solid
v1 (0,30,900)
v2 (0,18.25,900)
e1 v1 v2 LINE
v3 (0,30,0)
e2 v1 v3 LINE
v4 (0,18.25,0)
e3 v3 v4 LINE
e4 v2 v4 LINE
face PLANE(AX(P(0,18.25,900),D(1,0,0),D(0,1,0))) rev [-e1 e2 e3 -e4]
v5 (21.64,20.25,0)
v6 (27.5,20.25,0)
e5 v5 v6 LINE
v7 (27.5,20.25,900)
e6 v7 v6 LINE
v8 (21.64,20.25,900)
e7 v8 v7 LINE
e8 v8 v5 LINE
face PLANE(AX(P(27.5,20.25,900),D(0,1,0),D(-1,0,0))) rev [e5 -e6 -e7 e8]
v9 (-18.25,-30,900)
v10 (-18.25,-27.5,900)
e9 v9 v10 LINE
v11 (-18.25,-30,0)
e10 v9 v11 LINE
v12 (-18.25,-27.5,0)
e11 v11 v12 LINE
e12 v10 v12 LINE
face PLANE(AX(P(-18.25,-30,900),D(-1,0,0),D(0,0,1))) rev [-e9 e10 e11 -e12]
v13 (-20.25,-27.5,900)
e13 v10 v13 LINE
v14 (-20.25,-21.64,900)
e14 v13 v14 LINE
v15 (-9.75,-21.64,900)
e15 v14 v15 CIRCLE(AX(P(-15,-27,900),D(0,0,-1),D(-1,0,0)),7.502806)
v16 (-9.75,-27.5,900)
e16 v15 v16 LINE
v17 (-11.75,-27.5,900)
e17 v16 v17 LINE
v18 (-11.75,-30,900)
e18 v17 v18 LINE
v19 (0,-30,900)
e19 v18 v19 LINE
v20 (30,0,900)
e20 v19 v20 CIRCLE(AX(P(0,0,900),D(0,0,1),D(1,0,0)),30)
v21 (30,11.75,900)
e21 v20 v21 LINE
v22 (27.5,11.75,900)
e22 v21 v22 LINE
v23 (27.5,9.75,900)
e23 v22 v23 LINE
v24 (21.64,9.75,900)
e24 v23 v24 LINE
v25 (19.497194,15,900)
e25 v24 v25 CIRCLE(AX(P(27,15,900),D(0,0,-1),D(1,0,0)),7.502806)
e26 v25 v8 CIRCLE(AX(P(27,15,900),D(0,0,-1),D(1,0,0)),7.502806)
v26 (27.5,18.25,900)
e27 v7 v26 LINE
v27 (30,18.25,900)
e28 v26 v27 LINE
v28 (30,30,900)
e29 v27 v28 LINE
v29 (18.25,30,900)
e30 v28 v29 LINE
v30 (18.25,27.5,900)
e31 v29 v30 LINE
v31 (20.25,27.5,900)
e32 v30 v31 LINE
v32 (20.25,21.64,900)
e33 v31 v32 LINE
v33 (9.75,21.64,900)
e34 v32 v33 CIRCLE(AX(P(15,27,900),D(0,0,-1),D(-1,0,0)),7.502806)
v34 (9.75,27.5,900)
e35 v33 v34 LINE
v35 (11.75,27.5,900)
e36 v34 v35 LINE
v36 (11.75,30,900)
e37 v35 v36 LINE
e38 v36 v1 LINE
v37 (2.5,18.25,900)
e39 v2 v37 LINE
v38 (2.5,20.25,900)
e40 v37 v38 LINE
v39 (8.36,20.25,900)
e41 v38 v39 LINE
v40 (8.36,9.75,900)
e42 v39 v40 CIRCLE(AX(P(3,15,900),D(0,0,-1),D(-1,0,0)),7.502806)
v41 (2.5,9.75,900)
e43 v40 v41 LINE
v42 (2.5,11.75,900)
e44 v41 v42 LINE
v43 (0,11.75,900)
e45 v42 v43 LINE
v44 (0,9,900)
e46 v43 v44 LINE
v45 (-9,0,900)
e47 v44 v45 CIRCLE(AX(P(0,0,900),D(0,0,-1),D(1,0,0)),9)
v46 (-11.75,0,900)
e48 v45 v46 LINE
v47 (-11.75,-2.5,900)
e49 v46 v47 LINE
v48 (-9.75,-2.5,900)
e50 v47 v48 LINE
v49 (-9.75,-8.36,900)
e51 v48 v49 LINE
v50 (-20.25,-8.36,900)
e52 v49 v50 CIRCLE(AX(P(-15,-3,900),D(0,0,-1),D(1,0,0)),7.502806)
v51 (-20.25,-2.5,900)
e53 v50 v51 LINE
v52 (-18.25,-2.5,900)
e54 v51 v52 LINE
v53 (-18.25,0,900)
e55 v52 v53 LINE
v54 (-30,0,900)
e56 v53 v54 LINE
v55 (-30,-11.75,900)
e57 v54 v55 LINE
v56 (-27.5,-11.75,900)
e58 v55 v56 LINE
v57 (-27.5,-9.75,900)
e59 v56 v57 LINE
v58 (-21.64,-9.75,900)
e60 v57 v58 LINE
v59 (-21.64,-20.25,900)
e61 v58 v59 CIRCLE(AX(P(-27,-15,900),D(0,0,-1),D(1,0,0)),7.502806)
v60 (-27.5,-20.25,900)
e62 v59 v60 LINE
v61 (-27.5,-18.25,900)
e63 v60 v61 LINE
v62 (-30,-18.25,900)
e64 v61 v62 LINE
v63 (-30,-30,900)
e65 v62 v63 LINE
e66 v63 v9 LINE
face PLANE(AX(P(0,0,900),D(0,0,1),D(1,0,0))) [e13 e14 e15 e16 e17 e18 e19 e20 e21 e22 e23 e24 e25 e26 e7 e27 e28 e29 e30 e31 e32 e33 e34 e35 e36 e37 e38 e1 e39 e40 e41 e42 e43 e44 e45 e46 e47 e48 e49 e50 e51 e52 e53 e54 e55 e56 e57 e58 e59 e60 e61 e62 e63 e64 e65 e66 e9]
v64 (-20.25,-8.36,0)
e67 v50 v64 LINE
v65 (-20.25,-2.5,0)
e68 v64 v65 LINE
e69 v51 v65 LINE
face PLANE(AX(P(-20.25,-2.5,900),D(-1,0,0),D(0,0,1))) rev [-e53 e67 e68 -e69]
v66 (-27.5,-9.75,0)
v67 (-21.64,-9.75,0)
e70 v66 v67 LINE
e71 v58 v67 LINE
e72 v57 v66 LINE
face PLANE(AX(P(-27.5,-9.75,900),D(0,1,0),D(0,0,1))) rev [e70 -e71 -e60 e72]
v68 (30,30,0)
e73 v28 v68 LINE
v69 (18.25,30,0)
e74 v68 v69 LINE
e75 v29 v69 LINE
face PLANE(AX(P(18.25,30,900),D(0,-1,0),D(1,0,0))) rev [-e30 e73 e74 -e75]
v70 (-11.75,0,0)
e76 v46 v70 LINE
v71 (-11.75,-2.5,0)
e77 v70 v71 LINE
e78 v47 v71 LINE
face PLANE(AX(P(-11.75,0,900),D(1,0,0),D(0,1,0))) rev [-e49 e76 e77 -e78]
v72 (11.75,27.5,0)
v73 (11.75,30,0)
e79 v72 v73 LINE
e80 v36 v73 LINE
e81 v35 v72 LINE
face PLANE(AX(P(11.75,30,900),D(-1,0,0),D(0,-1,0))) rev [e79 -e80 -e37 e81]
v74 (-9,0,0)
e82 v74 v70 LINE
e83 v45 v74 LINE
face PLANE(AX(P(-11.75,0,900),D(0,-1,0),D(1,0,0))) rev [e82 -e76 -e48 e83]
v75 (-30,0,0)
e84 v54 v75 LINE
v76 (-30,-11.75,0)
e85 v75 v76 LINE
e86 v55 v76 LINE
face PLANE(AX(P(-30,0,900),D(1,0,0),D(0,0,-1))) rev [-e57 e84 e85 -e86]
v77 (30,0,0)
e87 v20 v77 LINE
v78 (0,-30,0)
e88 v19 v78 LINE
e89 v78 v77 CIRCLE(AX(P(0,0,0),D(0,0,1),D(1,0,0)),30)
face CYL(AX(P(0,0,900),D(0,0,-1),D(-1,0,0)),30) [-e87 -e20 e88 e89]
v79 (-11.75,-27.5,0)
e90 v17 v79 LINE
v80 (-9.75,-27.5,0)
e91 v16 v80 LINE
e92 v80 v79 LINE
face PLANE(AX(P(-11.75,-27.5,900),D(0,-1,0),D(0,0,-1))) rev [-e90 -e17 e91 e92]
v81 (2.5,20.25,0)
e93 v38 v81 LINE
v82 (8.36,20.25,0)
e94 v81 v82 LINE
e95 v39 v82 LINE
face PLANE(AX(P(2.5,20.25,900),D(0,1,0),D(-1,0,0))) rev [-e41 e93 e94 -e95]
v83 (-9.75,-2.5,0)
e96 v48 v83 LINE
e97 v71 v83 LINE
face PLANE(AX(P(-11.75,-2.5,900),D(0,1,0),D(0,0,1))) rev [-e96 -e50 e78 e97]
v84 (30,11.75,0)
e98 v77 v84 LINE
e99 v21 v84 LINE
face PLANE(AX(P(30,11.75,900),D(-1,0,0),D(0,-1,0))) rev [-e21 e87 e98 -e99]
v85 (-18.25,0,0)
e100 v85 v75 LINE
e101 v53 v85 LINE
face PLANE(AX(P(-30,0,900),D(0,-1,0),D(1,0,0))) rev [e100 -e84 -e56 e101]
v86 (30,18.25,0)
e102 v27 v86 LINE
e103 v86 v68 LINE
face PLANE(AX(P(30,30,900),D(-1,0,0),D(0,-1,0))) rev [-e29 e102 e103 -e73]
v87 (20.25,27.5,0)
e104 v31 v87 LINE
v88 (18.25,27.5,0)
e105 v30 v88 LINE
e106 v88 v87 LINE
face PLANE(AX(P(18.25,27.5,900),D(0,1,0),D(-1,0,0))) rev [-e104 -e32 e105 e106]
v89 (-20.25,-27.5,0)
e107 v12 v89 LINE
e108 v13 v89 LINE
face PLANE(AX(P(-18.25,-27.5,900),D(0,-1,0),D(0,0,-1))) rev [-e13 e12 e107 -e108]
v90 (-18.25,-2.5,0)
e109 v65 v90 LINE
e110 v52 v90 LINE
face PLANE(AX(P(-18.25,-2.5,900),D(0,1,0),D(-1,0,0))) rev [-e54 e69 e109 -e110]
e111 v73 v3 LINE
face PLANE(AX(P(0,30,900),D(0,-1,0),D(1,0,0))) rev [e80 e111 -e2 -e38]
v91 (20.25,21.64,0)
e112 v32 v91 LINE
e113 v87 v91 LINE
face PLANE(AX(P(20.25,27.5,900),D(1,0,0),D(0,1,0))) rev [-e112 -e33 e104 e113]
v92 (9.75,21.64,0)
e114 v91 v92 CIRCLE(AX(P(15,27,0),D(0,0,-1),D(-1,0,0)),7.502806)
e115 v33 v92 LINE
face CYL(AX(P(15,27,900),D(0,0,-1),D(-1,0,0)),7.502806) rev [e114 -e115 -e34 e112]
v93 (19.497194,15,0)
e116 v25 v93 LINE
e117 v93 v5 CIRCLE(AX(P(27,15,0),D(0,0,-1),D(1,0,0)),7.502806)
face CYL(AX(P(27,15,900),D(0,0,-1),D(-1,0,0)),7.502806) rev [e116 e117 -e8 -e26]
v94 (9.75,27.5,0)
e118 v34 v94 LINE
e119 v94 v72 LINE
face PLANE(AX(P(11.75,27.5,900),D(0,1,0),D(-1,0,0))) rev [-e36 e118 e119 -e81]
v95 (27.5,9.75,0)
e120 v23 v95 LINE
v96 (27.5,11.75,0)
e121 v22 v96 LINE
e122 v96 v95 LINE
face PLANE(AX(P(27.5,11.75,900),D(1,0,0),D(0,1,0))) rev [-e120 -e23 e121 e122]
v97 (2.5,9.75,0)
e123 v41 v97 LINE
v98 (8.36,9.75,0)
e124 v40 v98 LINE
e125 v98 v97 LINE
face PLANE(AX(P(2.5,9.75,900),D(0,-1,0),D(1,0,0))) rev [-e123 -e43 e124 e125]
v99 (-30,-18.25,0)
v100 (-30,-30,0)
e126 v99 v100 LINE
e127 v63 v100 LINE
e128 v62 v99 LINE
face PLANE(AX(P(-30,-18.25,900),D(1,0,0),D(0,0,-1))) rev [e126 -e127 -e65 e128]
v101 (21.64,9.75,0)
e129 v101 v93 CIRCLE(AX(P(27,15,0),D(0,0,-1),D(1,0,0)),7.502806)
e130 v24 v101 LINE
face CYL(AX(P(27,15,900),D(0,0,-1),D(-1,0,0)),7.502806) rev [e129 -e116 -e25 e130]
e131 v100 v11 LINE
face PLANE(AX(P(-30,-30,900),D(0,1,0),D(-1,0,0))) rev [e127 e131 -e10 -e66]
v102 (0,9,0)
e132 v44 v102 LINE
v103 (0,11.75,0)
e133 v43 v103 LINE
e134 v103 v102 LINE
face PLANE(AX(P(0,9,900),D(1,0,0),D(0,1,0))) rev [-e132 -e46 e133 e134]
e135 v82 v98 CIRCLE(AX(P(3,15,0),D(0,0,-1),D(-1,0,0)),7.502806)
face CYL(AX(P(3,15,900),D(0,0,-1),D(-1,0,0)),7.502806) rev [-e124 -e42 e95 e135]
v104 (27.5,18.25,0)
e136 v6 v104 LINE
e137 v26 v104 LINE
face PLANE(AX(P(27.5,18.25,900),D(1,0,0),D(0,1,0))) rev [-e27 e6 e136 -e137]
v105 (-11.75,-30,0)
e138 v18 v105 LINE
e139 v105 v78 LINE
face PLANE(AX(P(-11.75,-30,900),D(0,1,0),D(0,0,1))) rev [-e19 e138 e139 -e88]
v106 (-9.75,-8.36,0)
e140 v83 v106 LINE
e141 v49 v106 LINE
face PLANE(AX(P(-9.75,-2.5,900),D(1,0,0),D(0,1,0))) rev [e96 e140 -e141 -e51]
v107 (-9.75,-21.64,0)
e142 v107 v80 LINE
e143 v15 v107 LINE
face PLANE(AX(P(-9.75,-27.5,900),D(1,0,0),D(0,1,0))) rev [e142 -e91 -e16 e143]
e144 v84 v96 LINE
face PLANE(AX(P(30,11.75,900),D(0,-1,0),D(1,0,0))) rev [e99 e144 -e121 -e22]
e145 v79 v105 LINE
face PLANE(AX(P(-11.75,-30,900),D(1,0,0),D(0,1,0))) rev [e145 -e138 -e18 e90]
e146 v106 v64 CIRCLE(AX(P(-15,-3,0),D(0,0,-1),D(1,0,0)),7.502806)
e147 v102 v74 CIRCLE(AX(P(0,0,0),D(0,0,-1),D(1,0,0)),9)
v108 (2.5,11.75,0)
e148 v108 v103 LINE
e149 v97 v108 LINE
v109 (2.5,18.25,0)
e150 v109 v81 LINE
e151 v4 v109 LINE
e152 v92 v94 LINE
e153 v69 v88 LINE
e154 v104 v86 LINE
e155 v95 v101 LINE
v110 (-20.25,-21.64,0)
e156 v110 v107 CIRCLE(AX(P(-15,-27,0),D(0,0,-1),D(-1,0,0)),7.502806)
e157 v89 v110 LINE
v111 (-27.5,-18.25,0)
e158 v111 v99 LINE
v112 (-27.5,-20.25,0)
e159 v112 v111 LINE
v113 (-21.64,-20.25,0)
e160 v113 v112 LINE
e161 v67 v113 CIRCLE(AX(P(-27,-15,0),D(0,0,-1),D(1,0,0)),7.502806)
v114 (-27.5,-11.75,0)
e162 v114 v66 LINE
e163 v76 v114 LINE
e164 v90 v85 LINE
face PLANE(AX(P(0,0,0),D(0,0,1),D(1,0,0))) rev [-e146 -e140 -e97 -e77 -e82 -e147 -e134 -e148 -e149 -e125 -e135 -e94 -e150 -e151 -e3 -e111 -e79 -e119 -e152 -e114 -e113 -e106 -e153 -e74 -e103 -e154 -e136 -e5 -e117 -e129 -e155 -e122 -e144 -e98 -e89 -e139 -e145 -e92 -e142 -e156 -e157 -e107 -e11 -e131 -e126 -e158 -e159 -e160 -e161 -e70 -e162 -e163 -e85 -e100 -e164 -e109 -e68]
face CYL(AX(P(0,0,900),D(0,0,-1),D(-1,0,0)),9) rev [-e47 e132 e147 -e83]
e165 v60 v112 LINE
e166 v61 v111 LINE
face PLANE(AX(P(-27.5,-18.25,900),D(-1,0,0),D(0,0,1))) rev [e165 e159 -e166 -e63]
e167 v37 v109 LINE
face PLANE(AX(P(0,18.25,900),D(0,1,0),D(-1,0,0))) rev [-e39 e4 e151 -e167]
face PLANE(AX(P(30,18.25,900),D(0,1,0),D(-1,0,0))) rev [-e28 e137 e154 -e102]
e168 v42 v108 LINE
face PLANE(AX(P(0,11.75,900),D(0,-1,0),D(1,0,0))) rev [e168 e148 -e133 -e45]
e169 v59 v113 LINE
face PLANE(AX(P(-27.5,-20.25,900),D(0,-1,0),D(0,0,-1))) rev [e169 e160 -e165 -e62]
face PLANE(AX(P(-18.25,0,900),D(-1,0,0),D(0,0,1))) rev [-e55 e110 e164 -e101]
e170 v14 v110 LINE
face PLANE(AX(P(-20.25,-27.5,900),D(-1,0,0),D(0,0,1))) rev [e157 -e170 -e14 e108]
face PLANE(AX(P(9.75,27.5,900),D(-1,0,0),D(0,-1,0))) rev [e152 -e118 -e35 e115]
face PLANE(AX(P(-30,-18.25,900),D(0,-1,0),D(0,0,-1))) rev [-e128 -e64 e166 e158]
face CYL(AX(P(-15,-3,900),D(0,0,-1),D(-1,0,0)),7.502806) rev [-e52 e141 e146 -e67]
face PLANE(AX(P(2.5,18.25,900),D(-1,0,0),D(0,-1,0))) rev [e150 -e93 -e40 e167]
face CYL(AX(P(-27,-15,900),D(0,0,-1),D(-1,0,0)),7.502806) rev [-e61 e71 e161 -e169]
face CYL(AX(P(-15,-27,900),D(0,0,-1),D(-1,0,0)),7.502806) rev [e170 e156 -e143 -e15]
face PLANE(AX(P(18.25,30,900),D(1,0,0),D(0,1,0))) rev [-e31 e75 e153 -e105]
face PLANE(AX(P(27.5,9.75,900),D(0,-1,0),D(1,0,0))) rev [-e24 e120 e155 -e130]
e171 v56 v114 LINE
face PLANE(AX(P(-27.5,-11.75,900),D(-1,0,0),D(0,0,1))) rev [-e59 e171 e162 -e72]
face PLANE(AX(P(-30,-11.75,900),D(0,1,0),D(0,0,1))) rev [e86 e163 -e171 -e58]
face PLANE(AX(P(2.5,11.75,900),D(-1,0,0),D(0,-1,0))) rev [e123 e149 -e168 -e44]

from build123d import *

# Parameters (mm, degrees)
EXTRUDE_1_DEPTH = 900


with BuildPart() as part:
    # 草图1 → 凸台-拉伸1 (new body)
    with BuildSketch(Plane.XY):
        with BuildLine():
            Line((0, 9), (0, 11.75))
            Line((0, 11.75), (2.5, 11.75))
            Line((2.5, 11.75), (2.5, 9.75))
            Line((2.5, 9.75), (8.36, 9.75))
            ThreePointArc((8.36, 9.75), (10.502806142, 15), (8.36, 20.25))
            Line((8.36, 20.25), (2.5, 20.25))
            Line((2.5, 20.25), (2.5, 18.25))
            Line((2.5, 18.25), (0, 18.25))
            Line((0, 18.25), (0, 30))
            Line((0, 30), (11.75, 30))
            Line((11.75, 30), (11.75, 27.5))
            Line((11.75, 27.5), (9.75, 27.5))
            Line((9.75, 27.5), (9.75, 21.64))
            ThreePointArc((9.75, 21.64), (15, 19.497193858), (20.25, 21.64))
            Line((20.25, 21.64), (20.25, 27.5))
            Line((20.25, 27.5), (18.25, 27.5))
            Line((18.25, 27.5), (18.25, 30))
            Line((18.25, 30), (30, 30))
            Line((30, 30), (30, 18.25))
            Line((30, 18.25), (27.5, 18.25))
            Line((27.5, 18.25), (27.5, 20.25))
            Line((27.5, 20.25), (21.64, 20.25))
            ThreePointArc((21.64, 20.25), (19.497193858, 15), (21.64, 9.75))
            Line((21.64, 9.75), (27.5, 9.75))
            Line((27.5, 9.75), (27.5, 11.75))
            Line((27.5, 11.75), (30, 11.75))
            Line((30, 11.75), (30, 0))
            ThreePointArc((30, 0), (21.213203436, -21.213203436), (0, -30))
            Line((0, -30), (-11.75, -30))
            Line((-11.75, -30), (-11.75, -27.5))
            Line((-11.75, -27.5), (-9.75, -27.5))
            Line((-9.75, -27.5), (-9.75, -21.64))
            ThreePointArc((-9.75, -21.64), (-15, -19.497193858), (-20.25, -21.64))
            Line((-20.25, -21.64), (-20.25, -27.5))
            Line((-20.25, -27.5), (-18.25, -27.5))
            Line((-18.25, -27.5), (-18.25, -30))
            Line((-18.25, -30), (-30, -30))
            Line((-30, -30), (-30, -18.25))
            Line((-30, -18.25), (-27.5, -18.25))
            Line((-27.5, -18.25), (-27.5, -20.25))
            Line((-27.5, -20.25), (-21.64, -20.25))
            ThreePointArc((-21.64, -20.25), (-19.497193858, -15), (-21.64, -9.75))
            Line((-21.64, -9.75), (-27.5, -9.75))
            Line((-27.5, -9.75), (-27.5, -11.75))
            Line((-27.5, -11.75), (-30, -11.75))
            Line((-30, -11.75), (-30, 0))
            Line((-30, 0), (-18.25, 0))
            Line((-18.25, 0), (-18.25, -2.5))
            Line((-18.25, -2.5), (-20.25, -2.5))
            Line((-20.25, -2.5), (-20.25, -8.36))
            ThreePointArc((-20.25, -8.36), (-15, -10.502806142), (-9.75, -8.36))
            Line((-9.75, -8.36), (-9.75, -2.5))
            Line((-9.75, -2.5), (-11.75, -2.5))
            Line((-11.75, -2.5), (-11.75, 0))
            Line((-11.75, 0), (-9, 0))
            ThreePointArc((-9, 0), (6.363961031, -6.363961031), (0, 9))
        make_face()
    extrude(amount=EXTRUDE_1_DEPTH)


solid = part.part
